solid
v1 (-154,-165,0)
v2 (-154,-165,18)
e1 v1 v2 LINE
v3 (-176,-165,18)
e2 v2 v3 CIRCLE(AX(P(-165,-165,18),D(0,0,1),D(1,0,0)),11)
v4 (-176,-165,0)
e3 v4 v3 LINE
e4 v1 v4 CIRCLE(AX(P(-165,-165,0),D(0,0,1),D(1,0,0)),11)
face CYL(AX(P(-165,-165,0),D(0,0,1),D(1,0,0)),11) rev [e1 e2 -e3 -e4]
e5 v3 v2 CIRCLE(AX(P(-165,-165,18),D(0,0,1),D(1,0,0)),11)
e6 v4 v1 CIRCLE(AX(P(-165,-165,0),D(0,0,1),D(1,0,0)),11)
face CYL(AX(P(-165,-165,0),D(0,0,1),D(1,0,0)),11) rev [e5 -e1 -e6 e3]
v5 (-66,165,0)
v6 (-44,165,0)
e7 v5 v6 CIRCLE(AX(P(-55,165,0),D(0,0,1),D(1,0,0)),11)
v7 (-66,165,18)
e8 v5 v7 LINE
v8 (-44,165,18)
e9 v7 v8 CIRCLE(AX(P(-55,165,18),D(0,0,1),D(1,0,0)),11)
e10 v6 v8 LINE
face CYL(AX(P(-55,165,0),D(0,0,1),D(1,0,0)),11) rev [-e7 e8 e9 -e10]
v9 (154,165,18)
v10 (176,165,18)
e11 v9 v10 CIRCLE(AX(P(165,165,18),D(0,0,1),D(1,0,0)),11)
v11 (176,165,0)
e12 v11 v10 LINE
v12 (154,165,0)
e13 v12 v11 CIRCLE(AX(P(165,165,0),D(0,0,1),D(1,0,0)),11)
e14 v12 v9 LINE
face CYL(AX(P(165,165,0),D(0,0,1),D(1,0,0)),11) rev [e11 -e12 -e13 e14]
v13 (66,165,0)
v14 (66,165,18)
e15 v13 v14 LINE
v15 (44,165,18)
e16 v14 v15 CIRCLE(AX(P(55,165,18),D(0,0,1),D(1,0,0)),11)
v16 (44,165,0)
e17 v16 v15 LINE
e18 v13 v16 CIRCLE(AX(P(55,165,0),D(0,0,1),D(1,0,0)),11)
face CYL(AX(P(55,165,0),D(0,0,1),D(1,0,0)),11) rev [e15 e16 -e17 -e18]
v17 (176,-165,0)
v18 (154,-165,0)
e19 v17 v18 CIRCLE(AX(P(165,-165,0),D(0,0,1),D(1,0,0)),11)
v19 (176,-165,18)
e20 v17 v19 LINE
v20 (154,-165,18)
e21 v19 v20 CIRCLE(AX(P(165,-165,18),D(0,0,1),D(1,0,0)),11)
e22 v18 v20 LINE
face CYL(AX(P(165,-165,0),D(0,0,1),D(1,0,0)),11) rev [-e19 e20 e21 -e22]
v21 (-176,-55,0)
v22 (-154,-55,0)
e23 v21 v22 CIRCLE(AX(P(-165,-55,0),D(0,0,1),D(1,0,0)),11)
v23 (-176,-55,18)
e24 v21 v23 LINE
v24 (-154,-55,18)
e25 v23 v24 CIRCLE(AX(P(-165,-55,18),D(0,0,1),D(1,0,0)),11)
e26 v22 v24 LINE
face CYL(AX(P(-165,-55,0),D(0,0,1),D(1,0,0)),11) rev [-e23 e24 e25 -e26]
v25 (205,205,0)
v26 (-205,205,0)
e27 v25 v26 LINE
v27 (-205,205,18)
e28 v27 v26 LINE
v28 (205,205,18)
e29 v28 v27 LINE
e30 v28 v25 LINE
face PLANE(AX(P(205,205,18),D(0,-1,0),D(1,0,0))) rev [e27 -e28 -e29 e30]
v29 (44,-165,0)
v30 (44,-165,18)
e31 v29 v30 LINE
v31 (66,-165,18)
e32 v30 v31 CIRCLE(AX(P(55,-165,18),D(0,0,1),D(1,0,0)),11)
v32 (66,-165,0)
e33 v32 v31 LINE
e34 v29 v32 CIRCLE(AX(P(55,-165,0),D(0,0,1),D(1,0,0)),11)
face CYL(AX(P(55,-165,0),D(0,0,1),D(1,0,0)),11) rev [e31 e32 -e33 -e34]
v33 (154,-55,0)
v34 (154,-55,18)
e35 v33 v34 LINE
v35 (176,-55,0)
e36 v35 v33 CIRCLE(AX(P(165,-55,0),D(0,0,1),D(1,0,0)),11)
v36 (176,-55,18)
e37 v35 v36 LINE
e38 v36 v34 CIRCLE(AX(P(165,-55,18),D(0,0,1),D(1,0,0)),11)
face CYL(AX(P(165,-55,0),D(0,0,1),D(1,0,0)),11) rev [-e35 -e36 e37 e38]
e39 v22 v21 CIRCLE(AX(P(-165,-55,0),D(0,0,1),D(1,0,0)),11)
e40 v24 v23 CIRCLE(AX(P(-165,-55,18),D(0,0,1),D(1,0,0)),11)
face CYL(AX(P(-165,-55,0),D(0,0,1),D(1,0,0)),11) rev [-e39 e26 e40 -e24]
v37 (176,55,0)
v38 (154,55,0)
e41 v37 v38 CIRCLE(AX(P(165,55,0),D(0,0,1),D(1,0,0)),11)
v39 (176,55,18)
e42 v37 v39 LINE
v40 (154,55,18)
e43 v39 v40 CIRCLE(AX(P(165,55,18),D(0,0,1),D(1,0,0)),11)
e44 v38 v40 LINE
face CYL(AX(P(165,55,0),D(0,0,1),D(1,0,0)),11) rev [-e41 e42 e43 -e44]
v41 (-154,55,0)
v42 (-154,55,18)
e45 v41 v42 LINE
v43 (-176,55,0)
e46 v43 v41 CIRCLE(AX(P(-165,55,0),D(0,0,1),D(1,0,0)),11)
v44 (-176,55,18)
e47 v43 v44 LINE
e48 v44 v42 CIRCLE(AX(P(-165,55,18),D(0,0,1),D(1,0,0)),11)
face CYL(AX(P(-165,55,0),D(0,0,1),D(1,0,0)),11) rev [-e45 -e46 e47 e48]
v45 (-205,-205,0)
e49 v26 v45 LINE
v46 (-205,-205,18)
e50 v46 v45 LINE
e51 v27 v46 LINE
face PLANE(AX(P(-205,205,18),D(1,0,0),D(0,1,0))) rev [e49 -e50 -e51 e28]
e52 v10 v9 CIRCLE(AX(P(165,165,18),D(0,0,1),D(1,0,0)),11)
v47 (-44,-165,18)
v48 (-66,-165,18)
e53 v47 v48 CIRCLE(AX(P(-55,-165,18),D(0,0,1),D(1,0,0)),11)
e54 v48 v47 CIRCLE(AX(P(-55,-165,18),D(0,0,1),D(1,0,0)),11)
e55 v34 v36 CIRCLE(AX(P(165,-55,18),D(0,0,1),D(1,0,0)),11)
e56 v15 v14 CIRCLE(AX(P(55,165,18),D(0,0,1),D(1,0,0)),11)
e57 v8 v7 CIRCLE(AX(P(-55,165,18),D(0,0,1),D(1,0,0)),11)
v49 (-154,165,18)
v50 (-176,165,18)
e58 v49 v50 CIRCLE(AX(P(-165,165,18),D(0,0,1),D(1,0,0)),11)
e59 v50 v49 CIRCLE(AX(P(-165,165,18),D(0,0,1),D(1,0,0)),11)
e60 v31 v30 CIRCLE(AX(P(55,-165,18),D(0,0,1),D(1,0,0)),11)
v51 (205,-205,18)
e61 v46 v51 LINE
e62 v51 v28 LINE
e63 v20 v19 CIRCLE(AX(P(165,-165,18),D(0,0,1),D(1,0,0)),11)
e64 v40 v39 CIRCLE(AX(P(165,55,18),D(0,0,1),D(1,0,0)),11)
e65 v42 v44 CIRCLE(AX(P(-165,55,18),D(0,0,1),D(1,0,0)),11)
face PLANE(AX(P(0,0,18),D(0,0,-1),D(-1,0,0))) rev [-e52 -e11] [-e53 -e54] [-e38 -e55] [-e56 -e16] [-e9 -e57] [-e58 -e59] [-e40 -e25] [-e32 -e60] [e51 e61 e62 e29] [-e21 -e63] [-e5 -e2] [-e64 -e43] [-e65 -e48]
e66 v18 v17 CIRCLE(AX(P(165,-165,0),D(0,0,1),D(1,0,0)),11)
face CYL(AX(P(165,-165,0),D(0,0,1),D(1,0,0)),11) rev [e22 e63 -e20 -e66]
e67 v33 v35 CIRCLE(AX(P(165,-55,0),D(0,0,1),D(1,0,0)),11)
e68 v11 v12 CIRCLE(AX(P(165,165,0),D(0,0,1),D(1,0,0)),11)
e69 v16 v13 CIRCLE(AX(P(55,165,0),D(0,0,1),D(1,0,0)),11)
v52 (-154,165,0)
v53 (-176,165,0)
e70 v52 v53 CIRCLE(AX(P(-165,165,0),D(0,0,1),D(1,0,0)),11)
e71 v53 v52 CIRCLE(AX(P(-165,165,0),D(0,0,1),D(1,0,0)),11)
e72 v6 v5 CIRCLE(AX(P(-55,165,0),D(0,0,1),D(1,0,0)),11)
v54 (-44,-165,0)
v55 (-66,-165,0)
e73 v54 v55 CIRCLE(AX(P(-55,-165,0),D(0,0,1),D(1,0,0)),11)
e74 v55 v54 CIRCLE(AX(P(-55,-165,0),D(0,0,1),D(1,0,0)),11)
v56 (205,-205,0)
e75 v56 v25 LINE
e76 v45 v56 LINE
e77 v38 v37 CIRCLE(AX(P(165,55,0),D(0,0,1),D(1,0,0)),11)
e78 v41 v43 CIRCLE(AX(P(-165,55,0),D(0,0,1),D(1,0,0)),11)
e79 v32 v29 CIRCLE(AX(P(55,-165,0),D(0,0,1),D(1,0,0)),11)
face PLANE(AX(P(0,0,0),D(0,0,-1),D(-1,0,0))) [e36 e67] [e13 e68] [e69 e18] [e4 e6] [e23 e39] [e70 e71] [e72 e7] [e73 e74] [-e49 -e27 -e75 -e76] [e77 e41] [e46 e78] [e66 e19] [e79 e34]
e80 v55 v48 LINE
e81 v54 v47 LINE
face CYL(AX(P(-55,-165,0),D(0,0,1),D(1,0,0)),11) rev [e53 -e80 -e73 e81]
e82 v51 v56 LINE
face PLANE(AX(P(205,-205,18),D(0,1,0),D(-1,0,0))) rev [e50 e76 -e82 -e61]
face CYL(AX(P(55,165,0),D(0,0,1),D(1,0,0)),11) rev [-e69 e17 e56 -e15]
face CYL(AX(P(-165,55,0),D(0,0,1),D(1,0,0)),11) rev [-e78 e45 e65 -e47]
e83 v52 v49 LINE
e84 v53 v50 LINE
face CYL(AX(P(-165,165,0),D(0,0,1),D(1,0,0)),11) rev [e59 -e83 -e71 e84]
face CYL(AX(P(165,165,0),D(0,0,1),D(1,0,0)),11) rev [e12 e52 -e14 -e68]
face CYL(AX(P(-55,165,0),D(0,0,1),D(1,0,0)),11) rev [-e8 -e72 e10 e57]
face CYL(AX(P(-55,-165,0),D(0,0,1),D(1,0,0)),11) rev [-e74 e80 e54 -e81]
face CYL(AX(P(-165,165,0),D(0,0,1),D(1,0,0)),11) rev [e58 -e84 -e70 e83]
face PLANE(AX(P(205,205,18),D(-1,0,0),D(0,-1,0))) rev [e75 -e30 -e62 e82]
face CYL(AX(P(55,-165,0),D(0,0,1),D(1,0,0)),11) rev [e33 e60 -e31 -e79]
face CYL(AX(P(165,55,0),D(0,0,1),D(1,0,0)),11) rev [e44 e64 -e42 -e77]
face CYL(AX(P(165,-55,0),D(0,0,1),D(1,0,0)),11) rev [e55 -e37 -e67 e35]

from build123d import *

# Parameters (mm, degrees)
SKETCH1_W           = 410
SKETCH1_H           = 410
BOSS_EXTRUDE1_DEPTH = 18
SKETCH2_R           = 11
CUT_EXTRUDE1_DEPTH  = 18


with BuildPart() as part:
    # Sketch1 → Boss-Extrude1 (new body)
    with BuildSketch(Plane.XY):
        Rectangle(SKETCH1_W, SKETCH1_H)
    extrude(amount=BOSS_EXTRUDE1_DEPTH)

    # Sketch2 → Cut-Extrude1 (cut)
    with BuildSketch(Plane.XY.offset(18)):
        with Locations((-165, 165)):
            Circle(SKETCH2_R)
        with Locations((165, 165)):
            Circle(SKETCH2_R)
        with Locations((165, -165)):
            Circle(SKETCH2_R)
        with Locations((-165, -165)):
            Circle(SKETCH2_R)
        with Locations((-165, 55)):
            Circle(SKETCH2_R)
        with Locations((-165, -55)):
            Circle(SKETCH2_R)
        with Locations((-55, 165)):
            Circle(SKETCH2_R)
        with Locations((55, 165)):
            Circle(SKETCH2_R)
        with Locations((165, 55)):
            Circle(SKETCH2_R)
        with Locations((165, -55)):
            Circle(SKETCH2_R)
        with Locations((-55, -165)):
            Circle(SKETCH2_R)
        with Locations((55, -165)):
            Circle(SKETCH2_R)
    extrude(amount=-CUT_EXTRUDE1_DEPTH, mode=Mode.SUBTRACT)


solid = part.part
